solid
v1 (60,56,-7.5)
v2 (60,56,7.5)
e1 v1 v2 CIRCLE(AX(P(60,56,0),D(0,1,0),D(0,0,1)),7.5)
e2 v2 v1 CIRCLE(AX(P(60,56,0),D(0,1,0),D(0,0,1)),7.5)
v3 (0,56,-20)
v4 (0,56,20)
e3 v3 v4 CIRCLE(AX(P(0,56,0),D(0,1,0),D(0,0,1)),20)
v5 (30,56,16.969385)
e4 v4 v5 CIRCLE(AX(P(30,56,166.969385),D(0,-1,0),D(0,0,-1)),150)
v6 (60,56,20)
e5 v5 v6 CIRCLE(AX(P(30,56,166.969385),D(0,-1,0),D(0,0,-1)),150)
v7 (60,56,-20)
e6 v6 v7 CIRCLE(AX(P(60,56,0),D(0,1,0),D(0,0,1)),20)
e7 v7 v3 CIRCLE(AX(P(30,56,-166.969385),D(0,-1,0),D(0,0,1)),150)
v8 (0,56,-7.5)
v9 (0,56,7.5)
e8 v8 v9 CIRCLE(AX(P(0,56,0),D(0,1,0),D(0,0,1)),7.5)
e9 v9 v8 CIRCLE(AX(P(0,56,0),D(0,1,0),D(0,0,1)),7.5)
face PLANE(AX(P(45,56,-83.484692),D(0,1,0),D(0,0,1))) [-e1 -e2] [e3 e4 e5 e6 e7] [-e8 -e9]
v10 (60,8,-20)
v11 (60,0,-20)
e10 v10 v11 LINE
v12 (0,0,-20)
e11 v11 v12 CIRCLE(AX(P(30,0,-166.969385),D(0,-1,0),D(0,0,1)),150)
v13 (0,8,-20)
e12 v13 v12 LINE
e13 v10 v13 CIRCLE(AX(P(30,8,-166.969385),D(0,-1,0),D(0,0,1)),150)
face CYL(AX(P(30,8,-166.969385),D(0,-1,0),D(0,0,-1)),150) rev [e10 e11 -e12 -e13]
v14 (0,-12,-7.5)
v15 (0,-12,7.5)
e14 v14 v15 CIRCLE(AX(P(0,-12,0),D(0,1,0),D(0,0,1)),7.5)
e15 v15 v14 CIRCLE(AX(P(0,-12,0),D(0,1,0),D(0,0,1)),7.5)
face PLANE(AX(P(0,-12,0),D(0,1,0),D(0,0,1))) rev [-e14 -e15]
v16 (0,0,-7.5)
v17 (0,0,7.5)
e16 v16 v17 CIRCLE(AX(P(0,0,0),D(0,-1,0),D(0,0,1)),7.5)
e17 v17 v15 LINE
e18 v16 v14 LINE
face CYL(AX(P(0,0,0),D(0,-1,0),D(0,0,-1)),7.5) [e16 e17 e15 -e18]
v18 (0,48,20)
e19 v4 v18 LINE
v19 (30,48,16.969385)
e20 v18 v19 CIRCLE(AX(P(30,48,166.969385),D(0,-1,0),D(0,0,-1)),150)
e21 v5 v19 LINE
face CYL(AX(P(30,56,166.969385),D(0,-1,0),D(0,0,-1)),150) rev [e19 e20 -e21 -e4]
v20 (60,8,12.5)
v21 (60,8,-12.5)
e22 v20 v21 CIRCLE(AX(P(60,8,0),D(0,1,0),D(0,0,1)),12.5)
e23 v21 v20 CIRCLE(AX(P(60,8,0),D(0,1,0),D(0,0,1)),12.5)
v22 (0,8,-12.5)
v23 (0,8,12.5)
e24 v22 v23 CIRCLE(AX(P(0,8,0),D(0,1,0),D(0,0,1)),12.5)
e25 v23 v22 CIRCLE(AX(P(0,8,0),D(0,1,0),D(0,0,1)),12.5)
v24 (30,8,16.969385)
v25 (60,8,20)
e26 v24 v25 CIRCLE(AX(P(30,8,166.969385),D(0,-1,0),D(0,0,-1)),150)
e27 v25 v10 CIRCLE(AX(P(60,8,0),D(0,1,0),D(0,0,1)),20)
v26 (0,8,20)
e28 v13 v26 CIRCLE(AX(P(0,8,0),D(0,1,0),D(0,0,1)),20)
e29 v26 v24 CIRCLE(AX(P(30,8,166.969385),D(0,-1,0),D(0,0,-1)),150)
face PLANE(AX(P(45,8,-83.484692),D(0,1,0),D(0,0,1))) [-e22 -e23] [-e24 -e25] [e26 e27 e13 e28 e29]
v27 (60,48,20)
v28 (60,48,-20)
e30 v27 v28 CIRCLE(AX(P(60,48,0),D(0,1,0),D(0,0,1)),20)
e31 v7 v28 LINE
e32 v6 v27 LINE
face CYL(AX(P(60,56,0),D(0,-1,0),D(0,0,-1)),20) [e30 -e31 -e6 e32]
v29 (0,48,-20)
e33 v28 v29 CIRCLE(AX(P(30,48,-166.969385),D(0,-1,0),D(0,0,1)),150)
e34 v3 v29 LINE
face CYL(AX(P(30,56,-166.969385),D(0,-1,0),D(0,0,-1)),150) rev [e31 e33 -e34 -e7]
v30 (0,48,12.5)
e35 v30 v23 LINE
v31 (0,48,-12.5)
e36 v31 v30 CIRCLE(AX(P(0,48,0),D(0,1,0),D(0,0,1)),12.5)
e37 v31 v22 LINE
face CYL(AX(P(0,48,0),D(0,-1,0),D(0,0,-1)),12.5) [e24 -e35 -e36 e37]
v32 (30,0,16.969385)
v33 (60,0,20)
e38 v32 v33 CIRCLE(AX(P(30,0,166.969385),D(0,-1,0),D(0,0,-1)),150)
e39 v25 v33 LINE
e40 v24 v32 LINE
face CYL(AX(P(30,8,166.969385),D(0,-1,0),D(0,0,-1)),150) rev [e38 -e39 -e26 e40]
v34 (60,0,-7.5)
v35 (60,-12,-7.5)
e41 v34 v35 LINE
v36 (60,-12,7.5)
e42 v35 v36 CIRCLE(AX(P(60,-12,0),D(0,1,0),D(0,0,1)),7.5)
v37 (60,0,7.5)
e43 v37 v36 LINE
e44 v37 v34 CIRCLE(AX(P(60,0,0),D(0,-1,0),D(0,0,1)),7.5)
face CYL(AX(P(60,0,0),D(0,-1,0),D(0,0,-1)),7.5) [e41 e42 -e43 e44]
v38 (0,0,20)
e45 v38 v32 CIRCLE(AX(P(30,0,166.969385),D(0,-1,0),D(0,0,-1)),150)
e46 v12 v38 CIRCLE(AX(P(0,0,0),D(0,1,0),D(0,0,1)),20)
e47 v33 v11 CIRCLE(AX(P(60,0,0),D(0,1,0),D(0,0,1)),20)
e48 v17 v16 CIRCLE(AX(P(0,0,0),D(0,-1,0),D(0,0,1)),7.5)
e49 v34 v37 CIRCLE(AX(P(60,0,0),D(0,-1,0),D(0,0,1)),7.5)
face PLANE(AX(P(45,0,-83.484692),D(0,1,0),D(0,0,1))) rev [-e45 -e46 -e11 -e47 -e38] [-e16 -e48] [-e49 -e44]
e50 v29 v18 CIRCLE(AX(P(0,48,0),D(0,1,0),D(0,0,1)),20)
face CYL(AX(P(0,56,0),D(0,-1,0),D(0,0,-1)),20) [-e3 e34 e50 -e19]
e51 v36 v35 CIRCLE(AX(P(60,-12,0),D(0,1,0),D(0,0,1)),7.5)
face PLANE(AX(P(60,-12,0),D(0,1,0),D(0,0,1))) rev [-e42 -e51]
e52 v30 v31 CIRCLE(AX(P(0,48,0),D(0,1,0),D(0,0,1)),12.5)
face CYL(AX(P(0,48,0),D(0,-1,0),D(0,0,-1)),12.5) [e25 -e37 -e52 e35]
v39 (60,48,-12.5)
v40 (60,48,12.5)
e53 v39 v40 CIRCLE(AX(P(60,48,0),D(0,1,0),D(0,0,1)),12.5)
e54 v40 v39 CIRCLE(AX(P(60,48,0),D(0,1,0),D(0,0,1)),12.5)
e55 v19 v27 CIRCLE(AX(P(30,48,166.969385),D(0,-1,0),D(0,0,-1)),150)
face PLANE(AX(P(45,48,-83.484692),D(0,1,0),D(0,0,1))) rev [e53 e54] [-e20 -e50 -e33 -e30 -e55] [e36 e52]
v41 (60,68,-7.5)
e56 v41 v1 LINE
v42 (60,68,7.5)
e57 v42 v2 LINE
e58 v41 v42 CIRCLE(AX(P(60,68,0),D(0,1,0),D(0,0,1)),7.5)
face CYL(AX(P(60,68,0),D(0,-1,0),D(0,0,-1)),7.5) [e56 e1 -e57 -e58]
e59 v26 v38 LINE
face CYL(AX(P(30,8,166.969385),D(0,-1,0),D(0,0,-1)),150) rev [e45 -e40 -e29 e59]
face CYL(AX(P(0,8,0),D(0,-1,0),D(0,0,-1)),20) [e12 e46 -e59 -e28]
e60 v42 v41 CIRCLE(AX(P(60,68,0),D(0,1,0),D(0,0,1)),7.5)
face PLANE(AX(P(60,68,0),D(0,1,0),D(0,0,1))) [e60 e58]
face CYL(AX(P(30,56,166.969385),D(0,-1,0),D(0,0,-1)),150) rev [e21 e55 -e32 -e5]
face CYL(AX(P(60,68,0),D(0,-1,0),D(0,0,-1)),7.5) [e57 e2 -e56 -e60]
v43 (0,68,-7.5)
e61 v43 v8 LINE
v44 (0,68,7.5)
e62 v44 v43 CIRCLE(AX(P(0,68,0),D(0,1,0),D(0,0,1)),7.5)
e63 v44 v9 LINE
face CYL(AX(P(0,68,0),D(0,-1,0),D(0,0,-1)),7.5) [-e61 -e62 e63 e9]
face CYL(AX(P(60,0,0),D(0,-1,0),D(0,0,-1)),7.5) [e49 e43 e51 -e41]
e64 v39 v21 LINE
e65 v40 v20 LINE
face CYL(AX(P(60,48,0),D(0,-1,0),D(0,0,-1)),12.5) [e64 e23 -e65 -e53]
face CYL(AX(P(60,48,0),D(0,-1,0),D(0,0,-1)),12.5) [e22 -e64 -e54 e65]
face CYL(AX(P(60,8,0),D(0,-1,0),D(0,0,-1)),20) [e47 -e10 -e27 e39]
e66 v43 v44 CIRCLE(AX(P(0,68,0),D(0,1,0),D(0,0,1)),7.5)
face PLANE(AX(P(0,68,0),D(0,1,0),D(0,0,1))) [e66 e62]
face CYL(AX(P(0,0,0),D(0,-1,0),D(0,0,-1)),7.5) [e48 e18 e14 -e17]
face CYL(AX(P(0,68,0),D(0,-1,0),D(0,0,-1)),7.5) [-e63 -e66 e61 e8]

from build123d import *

# Parameters (mm, degrees)
BOSS_EXTRUDE1_DEPTH = 8
SKETCH2_R           = 12.5
BOSS_EXTRUDE2_DEPTH = 40
LPATTERN1_COUNT     = 2
LPATTERN1_PITCH     = 48
SKETCH3_R           = 7.5
BOSS_EXTRUDE3_DEPTH = 12
LPATTERN2_COUNT     = 2
LPATTERN2_PITCH     = 68


with BuildPart() as part:
    # Sketch1 → Boss-Extrude1 (new body)
    with BuildSketch(Plane(origin=(0, 0, 0), x_dir=(1, 0, 0), z_dir=(0, 1, 0))):
        with BuildLine():
            ThreePointArc((0, 20), (-20, 0), (0, -20))
            ThreePointArc((0, -20), (30, -16.969384567), (60, -20))
            ThreePointArc((60, -20), (80, 0), (60, 20))
            ThreePointArc((60, 20), (30, 16.969384567), (0, 20))
        make_face()
    boss_extrude1 = extrude(amount=BOSS_EXTRUDE1_DEPTH)

    # Sketch2 → Boss-Extrude2 (add)
    with BuildSketch(Plane(origin=(0, 8, 0), x_dir=(1, 0, 0), z_dir=(0, 1, 0))):
        with Locations(Location((0, 0, 0), (0, 0, 270))):
            Circle(SKETCH2_R)
        with Locations(Location((60, 0, 0), (0, 0, 270))):
            Circle(SKETCH2_R)
    extrude(amount=BOSS_EXTRUDE2_DEPTH)

    # LPattern1: Boss-Extrude1 ×2
    with Locations(*[(0, i * LPATTERN1_PITCH, 0) for i in range(1, LPATTERN1_COUNT)]):
        add(boss_extrude1)

    # Sketch3 → Boss-Extrude3 (add)
    with BuildSketch(Plane(origin=(0, 56, 0), x_dir=(1, 0, 0), z_dir=(0, 1, 0))):
        with Locations(Location((0, 0, 0), (0, 0, 270))):
            Circle(SKETCH3_R)
        with Locations(Location((60, 0, 0), (0, 0, 270))):
            Circle(SKETCH3_R)
    boss_extrude3 = extrude(amount=BOSS_EXTRUDE3_DEPTH)

    # LPattern2: Boss-Extrude3 ×2
    with Locations(*[(0, -i * LPATTERN2_PITCH, 0) for i in range(1, LPATTERN2_COUNT)]):
        add(boss_extrude3)


solid = part.part
